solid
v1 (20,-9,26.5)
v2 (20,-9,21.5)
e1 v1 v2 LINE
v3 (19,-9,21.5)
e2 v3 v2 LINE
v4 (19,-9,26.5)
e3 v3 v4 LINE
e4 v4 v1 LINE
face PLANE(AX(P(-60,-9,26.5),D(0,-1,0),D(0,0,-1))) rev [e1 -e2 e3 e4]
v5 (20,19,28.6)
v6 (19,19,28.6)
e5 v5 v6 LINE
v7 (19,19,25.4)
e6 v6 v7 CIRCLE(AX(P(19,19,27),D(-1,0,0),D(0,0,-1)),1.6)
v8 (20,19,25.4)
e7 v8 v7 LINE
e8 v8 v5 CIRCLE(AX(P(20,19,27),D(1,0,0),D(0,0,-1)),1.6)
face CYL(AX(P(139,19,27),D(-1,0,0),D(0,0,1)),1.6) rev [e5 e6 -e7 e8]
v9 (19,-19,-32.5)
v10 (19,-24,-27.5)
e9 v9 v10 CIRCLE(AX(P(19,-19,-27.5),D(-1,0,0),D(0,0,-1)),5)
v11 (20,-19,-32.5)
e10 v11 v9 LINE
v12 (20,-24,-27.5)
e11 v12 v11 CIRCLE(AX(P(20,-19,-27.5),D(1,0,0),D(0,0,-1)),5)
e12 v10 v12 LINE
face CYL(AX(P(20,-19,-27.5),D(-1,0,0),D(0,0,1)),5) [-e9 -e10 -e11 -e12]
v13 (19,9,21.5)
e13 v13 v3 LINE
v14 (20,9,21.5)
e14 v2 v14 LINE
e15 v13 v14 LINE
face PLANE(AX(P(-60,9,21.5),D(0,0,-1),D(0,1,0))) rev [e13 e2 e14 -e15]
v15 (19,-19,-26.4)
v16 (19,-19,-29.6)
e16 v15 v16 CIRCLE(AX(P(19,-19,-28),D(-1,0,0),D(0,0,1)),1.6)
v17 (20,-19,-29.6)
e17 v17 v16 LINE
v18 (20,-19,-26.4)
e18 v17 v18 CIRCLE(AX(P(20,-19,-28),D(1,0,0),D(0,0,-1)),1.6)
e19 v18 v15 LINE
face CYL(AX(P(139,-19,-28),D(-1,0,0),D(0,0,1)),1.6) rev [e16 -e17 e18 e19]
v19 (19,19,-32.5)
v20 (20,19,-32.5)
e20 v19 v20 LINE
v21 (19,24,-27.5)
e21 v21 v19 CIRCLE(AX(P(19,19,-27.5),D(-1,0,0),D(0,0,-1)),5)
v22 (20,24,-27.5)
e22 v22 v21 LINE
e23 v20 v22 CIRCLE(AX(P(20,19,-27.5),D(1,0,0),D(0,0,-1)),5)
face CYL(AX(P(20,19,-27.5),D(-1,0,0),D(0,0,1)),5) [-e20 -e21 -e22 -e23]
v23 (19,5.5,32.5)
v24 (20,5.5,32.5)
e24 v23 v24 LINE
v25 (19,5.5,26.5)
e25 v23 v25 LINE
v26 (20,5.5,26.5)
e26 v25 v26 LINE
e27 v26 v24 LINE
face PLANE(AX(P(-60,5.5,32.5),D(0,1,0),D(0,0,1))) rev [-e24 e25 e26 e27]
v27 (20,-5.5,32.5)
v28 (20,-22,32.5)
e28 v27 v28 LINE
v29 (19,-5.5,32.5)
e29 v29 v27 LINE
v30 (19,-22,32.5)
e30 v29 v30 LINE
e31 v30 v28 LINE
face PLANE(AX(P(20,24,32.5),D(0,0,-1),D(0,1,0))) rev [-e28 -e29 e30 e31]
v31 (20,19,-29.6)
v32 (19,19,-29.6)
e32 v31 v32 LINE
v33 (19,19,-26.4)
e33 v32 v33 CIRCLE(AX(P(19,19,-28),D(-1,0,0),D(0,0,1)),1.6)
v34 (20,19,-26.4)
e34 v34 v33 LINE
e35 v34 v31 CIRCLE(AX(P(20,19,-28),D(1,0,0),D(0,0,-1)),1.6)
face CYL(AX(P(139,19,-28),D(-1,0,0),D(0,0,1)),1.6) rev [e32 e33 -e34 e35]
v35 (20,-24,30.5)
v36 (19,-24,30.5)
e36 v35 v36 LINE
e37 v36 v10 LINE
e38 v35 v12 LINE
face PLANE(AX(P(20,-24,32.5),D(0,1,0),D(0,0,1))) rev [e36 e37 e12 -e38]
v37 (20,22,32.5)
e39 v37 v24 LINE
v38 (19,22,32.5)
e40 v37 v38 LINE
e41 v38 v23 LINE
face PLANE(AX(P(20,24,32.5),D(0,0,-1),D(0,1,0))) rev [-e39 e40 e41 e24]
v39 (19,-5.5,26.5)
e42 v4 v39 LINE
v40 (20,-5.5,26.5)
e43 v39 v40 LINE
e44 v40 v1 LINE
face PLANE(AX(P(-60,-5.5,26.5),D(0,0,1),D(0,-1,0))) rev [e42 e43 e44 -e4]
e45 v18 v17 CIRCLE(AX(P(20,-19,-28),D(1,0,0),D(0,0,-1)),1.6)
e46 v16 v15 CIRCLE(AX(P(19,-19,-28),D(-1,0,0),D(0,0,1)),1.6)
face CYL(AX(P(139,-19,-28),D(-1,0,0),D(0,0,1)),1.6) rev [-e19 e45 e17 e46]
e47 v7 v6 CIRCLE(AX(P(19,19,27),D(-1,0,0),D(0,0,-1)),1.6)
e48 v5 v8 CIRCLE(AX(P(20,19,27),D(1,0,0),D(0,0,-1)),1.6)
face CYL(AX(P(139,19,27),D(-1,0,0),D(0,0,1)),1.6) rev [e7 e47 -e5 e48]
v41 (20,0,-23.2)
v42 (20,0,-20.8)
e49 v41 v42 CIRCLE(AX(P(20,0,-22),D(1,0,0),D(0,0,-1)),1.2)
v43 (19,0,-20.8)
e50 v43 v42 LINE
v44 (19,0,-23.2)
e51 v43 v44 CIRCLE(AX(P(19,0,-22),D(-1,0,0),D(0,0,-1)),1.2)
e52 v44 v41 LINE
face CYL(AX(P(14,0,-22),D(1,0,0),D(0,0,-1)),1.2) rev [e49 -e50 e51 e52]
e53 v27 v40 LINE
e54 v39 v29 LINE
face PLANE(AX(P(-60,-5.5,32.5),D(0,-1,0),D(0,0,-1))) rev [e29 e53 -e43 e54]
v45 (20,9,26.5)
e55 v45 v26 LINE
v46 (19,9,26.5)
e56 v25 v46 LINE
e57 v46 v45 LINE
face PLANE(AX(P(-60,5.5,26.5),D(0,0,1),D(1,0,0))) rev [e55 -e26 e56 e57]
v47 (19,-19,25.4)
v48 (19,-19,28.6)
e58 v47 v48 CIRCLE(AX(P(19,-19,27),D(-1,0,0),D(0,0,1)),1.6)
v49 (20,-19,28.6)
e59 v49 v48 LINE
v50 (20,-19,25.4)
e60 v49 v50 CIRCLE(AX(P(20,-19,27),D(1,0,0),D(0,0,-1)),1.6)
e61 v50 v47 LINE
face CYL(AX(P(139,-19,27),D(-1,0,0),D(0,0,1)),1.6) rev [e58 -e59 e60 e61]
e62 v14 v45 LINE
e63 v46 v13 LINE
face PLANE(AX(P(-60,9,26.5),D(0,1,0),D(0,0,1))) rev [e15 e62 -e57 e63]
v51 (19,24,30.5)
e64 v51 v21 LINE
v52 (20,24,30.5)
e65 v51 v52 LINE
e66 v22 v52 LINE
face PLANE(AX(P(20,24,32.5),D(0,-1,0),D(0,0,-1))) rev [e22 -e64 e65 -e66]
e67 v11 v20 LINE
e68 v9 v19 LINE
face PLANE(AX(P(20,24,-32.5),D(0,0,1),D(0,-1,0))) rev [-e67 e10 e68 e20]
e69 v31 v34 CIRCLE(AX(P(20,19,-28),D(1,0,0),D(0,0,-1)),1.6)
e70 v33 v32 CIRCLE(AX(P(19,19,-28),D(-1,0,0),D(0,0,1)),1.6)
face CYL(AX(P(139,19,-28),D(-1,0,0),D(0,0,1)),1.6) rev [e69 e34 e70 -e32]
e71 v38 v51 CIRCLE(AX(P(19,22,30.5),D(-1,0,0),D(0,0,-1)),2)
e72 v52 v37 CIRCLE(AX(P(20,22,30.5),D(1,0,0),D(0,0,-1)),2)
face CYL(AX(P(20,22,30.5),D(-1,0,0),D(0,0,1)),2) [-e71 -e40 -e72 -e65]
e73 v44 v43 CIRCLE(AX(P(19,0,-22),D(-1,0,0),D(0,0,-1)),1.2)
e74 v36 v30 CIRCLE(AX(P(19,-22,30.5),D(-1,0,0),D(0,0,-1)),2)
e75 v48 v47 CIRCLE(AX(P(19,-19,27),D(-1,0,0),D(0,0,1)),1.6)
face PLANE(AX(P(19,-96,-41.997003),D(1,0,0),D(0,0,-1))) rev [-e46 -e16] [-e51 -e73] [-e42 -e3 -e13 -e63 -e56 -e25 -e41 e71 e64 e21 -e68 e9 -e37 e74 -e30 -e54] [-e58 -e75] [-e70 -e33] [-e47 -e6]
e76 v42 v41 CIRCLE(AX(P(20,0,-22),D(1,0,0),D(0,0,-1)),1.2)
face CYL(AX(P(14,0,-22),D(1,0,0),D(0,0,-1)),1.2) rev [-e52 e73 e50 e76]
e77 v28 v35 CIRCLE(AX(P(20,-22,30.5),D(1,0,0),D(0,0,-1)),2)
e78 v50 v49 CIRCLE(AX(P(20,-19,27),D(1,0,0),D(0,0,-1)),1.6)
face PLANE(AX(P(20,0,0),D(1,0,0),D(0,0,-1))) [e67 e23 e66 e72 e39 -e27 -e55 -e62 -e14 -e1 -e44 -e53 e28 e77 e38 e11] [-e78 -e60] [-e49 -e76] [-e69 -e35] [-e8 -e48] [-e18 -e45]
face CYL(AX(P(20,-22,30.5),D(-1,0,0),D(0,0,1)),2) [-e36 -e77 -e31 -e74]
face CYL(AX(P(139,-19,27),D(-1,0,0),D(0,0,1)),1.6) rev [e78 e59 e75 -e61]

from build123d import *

# Parameters (mm, degrees)
SKETCH_1_W                = 65
SKETCH_1_H                = 48
EXTRUDE_1_DEPTH           = 20
SKETCH_2_W                = 6
SKETCH_2_H                = 27.1
CUT_EXTRUDE_1_DEPTH       = 80
CUT_EXTRUDE_2_DEPTH       = 80
SKETCH_4_R                = 1.2
CUT_EXTRUDE_3_DEPTH       = 6
HOLE_WIZARD_1_D           = 3.4
HOLE_WIZARD_1_CBORE_D     = 6
HOLE_WIZARD_1_CBORE_DEPTH = 5
FILLET_1_R                = 5
SKETCH_9_W                = 19.082133463
SKETCH_9_H                = 84.157101427
CUT_EXTRUDE_6_DEPTH       = 120
SKETCH_10_W               = 25.015989719
SKETCH_10_H               = 30.267159573
EXTRUDE_2_DEPTH           = 1
SKETCH_11_R               = 1.6
CUT_EXTRUDE_7_DEPTH       = 120
FILLET_2_R                = 2


with BuildPart() as part:
    # 草图1 → 凸台-拉伸1 (new body)
    with BuildSketch(Plane(origin=(0, 0, 0), x_dir=(0, 0, -1), z_dir=(1, 0, 0))):
        Rectangle(SKETCH_1_W, SKETCH_1_H)
    extrude(amount=EXTRUDE_1_DEPTH)

    # 草图2 → 切除-拉伸1 (cut)
    with BuildSketch(Plane(origin=(0, 0, -32.5), x_dir=(-1, 0, 0), z_dir=(0, 0, -1))):
        Rectangle(SKETCH_2_W, SKETCH_2_H)
    extrude(amount=-CUT_EXTRUDE_1_DEPTH, mode=Mode.SUBTRACT)

    # 草图3 → 切除-拉伸2 (cut)
    with BuildSketch(Plane(origin=(20, 0, 0), x_dir=(0, 0, -1), z_dir=(1, 0, 0))):
        Polygon((-26.5, -9), (-21.5, -9), (-21.5, 9), (-26.5, 9), (-26.5, 5.5), (-32.5, 5.5), (-32.5, -5.5), (-26.5, -5.5), align=None)
    extrude(amount=-CUT_EXTRUDE_2_DEPTH, mode=Mode.SUBTRACT)

    # 草图4 → 切除-拉伸3 (cut)
    with BuildSketch(Plane(origin=(20, 0, 0), x_dir=(0, 0, -1), z_dir=(1, 0, 0))):
        with Locations((22, 0)):
            Circle(SKETCH_4_R)
    extrude(amount=-CUT_EXTRUDE_3_DEPTH, mode=Mode.SUBTRACT)

    # 打孔尺寸(%根据)开槽圆柱头螺钉的类型1 (through all)
    with Locations(Plane(origin=(20, 0, 0), x_dir=(0, 0, -1), z_dir=(1, 0, 0))):
        with Locations((7.35, -10), (-7.65, -10), (-7.65, 10), (7.35, 10)):
            CounterBoreHole(HOLE_WIZARD_1_D / 2, HOLE_WIZARD_1_CBORE_D / 2, HOLE_WIZARD_1_CBORE_DEPTH)

    # 圆角1
    fillet_1_edges = [part.edges().sort_by_distance(p)[0] for p in [
        (10, -24, -32.5),
        (10, 24, -32.5),
    ]]
    fillet(fillet_1_edges, radius=FILLET_1_R)

    # 草图9 → 切除-拉伸6 (cut)
    with BuildSketch(Plane(origin=(0, 24, 0), x_dir=(1, 0, 0), z_dir=(0, 1, 0))):
        with Locations((9.458933268, -0.081547579)):
            Rectangle(SKETCH_9_W, SKETCH_9_H)
    extrude(amount=-CUT_EXTRUDE_6_DEPTH, mode=Mode.SUBTRACT)

    # 草图10 → 凸台-拉伸2 (add)
    with BuildSketch(Plane.ZY.offset(-19)):
        with Locations((0.80226206, -0.656396231)):
            Rectangle(SKETCH_10_W, SKETCH_10_H)
    extrude(amount=-EXTRUDE_2_DEPTH)

    # 草图11 → 切除-拉伸7 (cut)
    with BuildSketch(Plane.ZY.offset(-19)):
        with Locations((-28, 19)):
            Circle(SKETCH_11_R)
        with Locations((-28, -19)):
            Circle(SKETCH_11_R)
        with Locations((27, -19)):
            Circle(SKETCH_11_R)
        with Locations(Location((27, 19, 0), (0, 0, 180))):
            Circle(SKETCH_11_R)
    extrude(amount=-CUT_EXTRUDE_7_DEPTH, mode=Mode.SUBTRACT)

    # 圆角2
    fillet_2_edges = [part.edges().sort_by_distance(p)[0] for p in [
        (19.5, -24, 32.5),
        (19.5, 24, 32.5),
    ]]
    fillet(fillet_2_edges, radius=FILLET_2_R)


solid = part.part
